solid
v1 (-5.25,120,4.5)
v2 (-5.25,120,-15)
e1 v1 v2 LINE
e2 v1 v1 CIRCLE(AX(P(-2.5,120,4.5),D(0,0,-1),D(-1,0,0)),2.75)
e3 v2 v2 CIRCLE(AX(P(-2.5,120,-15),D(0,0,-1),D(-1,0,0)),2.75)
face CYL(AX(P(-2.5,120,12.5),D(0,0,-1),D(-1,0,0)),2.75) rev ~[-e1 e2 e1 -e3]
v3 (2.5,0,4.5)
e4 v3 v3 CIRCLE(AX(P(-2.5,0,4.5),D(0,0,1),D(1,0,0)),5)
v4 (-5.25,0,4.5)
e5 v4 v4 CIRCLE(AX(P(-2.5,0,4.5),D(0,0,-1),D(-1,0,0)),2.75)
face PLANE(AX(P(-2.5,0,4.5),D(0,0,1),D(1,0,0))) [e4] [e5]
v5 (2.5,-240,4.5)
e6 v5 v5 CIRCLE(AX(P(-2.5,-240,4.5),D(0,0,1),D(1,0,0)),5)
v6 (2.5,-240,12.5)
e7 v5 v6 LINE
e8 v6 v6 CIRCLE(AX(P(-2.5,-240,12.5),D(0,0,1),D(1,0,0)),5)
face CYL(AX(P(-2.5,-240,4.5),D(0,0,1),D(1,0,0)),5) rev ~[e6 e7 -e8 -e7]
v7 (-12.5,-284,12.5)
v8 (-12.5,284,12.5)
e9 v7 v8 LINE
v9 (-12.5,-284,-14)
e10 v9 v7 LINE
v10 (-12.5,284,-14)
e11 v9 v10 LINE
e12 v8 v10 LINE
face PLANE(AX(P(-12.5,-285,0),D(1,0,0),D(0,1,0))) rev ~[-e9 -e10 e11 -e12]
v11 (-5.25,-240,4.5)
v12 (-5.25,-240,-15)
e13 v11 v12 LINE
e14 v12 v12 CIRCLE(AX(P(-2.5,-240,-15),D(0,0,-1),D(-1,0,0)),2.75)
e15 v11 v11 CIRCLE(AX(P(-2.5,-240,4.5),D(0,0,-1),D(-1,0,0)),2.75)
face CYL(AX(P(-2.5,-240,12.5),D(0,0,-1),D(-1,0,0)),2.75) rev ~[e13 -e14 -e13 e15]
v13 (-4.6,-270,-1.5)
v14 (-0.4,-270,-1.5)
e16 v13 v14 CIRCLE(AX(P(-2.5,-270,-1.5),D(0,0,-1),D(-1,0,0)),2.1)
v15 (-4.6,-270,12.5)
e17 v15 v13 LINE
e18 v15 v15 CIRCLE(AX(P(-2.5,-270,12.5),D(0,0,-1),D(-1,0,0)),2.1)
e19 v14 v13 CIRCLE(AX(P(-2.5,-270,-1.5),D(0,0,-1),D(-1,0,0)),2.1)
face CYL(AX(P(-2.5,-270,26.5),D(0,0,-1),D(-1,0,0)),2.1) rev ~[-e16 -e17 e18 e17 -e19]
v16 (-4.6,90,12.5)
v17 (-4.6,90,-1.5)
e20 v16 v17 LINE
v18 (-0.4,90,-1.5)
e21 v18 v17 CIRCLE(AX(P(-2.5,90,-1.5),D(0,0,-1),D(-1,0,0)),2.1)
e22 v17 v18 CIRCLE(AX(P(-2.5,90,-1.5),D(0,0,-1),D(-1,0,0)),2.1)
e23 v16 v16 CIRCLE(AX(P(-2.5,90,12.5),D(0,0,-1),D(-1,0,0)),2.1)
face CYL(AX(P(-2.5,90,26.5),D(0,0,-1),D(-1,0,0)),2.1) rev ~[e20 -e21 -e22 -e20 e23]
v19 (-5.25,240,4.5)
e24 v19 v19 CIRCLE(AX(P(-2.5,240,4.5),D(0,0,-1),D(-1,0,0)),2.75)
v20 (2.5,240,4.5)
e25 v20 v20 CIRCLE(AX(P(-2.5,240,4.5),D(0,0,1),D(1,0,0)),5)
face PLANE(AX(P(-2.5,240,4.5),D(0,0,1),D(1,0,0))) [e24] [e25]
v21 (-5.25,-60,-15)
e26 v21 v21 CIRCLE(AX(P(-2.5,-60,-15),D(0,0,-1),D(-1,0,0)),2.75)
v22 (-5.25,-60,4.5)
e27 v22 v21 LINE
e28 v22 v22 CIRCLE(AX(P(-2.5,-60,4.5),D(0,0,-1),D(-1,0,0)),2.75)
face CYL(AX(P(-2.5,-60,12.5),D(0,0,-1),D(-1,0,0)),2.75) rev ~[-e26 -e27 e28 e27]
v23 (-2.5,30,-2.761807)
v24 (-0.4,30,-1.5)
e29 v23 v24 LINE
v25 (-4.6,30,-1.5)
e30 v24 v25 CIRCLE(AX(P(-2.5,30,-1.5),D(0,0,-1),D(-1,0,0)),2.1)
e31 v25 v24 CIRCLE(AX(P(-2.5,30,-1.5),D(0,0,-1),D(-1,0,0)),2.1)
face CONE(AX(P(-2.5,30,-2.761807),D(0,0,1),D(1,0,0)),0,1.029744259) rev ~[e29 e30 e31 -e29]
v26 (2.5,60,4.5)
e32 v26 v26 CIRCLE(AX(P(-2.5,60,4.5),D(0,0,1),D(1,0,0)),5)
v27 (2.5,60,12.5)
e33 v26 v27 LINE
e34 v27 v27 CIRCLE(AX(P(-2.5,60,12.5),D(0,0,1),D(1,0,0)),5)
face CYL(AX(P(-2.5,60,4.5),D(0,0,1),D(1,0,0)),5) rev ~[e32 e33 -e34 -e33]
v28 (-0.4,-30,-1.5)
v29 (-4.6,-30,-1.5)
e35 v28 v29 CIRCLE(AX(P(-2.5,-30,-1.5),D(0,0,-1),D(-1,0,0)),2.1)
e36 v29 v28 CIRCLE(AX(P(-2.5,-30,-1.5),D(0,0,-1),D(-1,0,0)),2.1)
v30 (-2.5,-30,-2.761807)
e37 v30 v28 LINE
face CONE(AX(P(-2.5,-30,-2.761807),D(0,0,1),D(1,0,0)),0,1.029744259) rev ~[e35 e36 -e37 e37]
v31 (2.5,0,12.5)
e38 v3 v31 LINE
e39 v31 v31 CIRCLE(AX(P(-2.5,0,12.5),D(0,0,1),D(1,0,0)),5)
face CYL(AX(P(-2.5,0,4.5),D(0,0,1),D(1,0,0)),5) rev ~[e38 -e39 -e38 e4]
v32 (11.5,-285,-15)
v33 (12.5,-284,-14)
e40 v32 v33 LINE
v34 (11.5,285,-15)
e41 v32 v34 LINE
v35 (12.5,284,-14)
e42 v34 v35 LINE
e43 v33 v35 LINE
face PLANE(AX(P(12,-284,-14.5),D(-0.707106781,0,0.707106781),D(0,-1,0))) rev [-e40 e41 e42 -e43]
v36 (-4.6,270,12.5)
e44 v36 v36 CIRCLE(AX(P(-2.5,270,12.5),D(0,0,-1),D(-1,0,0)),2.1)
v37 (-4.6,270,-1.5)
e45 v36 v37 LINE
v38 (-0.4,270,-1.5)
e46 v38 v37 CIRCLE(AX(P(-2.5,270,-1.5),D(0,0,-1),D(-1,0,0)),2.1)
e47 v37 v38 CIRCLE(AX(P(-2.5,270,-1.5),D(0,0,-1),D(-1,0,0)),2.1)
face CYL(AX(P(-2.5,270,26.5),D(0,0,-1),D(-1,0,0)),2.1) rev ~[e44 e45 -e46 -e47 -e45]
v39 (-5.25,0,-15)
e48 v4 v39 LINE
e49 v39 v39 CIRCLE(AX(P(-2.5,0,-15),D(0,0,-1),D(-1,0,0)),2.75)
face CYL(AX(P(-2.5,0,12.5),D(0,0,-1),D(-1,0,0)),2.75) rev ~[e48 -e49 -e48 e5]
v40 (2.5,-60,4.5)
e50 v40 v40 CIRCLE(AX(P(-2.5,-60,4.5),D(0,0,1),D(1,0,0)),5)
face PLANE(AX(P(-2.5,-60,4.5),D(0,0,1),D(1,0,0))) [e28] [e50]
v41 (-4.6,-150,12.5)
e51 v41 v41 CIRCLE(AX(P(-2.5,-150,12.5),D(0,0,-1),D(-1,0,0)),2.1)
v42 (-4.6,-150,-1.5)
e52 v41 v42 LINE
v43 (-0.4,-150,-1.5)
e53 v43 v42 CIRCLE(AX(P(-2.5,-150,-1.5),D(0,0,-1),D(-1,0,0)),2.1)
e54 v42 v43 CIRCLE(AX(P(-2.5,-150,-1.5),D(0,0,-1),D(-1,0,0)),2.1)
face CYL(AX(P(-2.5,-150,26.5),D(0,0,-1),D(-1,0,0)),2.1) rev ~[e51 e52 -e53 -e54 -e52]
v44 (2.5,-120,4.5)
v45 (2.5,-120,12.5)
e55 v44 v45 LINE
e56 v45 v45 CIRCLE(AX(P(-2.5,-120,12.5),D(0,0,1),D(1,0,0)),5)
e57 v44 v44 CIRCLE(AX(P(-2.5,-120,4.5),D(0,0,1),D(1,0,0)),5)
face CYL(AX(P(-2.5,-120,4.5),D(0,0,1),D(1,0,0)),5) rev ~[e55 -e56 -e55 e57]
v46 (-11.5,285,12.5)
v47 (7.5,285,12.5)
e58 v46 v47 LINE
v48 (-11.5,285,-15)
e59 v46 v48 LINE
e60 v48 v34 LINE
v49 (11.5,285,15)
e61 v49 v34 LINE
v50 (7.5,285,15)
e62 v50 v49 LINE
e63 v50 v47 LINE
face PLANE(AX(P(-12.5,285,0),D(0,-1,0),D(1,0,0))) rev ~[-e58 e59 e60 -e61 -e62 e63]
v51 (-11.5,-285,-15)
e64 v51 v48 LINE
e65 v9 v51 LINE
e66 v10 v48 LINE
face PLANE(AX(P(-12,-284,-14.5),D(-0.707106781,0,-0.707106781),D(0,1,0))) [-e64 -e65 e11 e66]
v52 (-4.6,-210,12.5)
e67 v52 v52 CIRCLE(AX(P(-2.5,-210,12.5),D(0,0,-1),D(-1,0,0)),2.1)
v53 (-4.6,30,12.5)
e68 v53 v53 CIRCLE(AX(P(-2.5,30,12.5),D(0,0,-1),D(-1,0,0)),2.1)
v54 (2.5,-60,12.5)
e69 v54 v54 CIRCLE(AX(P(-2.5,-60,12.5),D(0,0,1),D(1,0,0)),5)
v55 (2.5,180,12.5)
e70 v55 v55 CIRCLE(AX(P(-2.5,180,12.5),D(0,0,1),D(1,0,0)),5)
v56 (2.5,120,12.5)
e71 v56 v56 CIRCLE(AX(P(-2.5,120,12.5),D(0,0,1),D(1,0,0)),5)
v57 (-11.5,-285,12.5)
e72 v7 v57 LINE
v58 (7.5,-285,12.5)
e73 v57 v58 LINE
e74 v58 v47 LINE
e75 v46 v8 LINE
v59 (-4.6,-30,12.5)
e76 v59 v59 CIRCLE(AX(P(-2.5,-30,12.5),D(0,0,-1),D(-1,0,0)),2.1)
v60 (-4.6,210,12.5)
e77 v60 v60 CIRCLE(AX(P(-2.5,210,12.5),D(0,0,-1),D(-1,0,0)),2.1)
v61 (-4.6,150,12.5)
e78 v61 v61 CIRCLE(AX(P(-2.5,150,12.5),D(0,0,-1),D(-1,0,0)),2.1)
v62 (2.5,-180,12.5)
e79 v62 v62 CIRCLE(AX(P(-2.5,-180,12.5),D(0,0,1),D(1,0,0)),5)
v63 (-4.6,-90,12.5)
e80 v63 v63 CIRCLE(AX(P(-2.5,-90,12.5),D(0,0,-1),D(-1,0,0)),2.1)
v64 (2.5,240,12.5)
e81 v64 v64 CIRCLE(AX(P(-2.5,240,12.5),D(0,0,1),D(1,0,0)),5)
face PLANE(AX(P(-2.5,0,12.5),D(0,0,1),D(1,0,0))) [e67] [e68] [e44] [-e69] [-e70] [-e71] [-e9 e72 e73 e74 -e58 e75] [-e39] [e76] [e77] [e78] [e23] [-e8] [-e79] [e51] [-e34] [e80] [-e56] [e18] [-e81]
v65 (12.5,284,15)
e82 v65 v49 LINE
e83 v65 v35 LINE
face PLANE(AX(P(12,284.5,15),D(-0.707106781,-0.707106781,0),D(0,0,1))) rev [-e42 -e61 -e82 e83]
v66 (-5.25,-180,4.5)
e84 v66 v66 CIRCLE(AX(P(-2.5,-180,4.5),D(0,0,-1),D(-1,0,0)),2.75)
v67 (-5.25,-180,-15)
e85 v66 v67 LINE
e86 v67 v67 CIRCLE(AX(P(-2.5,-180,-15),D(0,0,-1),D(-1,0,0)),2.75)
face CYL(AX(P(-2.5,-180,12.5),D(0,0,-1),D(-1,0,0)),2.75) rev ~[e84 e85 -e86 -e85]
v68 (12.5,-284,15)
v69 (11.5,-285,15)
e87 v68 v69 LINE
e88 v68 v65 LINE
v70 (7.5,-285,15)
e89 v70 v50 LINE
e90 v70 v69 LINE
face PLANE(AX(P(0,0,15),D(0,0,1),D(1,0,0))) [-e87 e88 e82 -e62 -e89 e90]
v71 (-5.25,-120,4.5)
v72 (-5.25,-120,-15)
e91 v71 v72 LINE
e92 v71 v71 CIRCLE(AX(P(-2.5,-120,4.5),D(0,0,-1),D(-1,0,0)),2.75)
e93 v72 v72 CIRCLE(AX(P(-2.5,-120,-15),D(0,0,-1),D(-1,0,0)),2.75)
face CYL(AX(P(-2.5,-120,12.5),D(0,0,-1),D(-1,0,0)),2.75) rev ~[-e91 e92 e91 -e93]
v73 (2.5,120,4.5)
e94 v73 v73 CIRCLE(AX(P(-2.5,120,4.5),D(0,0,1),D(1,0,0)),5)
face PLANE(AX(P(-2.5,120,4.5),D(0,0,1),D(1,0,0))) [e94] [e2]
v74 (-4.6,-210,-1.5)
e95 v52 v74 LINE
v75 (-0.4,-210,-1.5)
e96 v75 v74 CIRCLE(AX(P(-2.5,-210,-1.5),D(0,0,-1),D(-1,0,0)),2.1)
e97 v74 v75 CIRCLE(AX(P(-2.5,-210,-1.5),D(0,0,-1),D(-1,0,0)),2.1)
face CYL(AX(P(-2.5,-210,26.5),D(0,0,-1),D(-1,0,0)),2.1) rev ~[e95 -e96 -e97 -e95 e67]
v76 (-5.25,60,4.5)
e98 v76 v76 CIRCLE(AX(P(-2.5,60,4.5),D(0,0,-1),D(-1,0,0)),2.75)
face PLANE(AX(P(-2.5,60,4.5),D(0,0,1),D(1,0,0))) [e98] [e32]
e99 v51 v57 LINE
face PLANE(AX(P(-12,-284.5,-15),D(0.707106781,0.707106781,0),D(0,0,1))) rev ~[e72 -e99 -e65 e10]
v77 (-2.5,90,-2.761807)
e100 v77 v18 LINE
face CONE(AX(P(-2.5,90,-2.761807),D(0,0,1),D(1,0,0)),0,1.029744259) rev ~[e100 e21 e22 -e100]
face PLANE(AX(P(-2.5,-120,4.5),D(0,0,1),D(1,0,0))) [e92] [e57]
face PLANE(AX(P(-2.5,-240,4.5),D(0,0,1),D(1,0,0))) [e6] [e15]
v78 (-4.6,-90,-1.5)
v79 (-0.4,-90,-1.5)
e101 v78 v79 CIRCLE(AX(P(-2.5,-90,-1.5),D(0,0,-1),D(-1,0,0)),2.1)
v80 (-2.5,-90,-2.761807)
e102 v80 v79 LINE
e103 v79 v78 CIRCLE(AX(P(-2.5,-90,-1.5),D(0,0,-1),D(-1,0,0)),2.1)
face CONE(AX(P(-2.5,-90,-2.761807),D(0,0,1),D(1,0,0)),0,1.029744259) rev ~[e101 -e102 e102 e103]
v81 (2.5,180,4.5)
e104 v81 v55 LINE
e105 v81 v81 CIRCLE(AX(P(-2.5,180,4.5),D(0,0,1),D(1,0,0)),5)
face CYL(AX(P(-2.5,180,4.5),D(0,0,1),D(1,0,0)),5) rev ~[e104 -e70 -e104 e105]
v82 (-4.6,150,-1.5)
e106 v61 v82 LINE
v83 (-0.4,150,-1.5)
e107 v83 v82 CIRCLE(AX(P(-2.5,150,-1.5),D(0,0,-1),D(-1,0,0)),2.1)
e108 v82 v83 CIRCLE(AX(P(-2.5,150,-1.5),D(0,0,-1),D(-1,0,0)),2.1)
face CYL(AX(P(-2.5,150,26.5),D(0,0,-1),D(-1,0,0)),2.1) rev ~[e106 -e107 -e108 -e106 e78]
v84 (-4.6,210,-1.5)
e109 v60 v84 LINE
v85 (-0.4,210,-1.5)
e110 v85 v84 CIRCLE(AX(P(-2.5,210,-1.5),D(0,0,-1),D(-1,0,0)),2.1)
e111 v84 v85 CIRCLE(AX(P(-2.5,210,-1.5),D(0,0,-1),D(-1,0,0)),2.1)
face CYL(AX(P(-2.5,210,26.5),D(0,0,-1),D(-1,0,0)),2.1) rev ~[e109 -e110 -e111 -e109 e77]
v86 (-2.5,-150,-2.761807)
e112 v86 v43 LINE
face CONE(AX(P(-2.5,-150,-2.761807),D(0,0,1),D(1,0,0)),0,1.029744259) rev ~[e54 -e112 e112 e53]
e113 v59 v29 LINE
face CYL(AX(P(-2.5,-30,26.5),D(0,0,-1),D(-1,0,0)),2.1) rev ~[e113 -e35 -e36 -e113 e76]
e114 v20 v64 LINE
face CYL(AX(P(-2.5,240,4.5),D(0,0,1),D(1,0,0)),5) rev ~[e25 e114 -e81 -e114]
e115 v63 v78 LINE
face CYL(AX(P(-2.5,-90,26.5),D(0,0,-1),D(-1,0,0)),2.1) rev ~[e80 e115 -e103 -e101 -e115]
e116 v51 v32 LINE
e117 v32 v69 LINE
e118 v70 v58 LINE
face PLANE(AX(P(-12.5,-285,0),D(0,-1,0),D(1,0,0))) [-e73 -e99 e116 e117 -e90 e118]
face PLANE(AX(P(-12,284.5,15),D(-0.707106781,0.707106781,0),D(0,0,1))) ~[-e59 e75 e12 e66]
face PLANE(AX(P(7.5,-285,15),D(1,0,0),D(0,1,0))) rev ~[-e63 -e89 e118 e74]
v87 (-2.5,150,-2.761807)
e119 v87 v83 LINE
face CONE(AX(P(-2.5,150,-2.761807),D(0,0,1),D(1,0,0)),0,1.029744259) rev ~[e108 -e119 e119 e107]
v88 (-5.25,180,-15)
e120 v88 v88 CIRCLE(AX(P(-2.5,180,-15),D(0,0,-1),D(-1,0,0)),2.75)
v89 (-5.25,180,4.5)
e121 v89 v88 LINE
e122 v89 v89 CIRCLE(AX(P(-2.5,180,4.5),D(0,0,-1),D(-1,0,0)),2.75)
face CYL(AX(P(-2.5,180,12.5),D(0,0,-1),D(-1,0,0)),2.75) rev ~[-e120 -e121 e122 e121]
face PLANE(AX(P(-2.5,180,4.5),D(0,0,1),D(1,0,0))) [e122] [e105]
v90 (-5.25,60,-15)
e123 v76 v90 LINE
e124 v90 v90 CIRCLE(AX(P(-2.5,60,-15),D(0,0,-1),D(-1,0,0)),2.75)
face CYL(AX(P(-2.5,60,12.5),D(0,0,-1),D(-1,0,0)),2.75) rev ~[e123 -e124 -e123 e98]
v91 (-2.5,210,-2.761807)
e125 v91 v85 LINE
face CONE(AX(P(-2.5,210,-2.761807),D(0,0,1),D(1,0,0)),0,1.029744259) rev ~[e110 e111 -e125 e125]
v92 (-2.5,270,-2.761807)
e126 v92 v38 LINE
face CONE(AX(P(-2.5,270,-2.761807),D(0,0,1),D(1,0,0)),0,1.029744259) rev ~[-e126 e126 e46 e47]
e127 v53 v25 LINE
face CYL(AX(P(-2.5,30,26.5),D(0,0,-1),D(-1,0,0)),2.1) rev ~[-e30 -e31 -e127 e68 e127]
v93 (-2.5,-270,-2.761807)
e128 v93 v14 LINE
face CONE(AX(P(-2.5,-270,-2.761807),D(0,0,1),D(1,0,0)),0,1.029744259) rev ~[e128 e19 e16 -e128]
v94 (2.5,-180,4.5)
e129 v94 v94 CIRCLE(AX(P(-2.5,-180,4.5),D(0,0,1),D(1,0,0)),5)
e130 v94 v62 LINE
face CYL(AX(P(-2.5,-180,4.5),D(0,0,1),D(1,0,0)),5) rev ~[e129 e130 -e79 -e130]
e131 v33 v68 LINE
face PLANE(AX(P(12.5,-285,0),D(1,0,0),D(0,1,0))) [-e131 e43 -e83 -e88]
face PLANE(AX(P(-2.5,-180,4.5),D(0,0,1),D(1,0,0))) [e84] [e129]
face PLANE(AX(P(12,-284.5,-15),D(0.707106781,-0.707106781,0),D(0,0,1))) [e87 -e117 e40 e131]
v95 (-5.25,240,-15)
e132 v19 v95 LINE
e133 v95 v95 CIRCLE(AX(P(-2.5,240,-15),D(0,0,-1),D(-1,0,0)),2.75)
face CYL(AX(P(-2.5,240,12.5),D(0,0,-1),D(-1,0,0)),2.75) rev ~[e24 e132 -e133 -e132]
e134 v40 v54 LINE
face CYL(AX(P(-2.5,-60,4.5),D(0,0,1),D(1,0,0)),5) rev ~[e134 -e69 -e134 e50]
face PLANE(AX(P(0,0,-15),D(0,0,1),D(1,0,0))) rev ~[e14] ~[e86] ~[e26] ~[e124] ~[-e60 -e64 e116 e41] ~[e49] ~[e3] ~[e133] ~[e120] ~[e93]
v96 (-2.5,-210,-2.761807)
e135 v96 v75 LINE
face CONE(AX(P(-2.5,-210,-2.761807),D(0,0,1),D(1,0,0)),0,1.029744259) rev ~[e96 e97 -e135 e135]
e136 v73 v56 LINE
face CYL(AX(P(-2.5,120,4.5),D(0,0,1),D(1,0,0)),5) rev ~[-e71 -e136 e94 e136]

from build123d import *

# Parameters (mm, degrees)
SKETCH1_W                                           = 25
SKETCH1_H                                           = 570
EXTRUDE1_DEPTH                                      = 15
CHAMFER1_SIZE                                       = 1
SKETCH_1_W                                          = 20
SKETCH_1_H                                          = 570
CUT_EXTRUDE1_DEPTH                                  = 2.5
CHAMFER2_SIZE                                       = 1
M5_TAPPED_HOLE1_D                                   = 4.2
M5_TAPPED_HOLE1_DEPTH                               = 14
M5_TAPPED_HOLE1_TIP                                 = 1.2618073
HOLE_SIZE_PER_SOCKET_HEAD_CAP_SCREW_TYP_D           = 5.5
HOLE_SIZE_PER_SOCKET_HEAD_CAP_SCREW_TYP_CBORE_D     = 10
HOLE_SIZE_PER_SOCKET_HEAD_CAP_SCREW_TYP_CBORE_DEPTH = 8
LPATTERN1_COUNT                                     = 9
LPATTERN1_PITCH                                     = 60


with BuildPart() as part:
    # Sketch1 → Extrude1 (new, symmetric)
    with BuildSketch(Plane.XY):
        Rectangle(SKETCH1_W, SKETCH1_H)
    extrude(amount=EXTRUDE1_DEPTH, both=True)

    # Chamfer1
    chamfer1_edges = [part.edges().sort_by_distance(p)[0] for p in [
        (-12.5, 285, 0),
        (12.5, 285, 0),
        (12.5, -285, 0),
        (-12.5, -285, 0),
    ]]
    chamfer(chamfer1_edges, length=CHAMFER1_SIZE)

    # 草图1 → Cut-Extrude1 (cut)
    with BuildSketch(Plane.XY.offset(15)):
        with Locations((-2.5, 0)):
            Rectangle(SKETCH_1_W, SKETCH_1_H)
    extrude(amount=-CUT_EXTRUDE1_DEPTH, mode=Mode.SUBTRACT)

    # Chamfer2
    chamfer2_edges = [part.edges().sort_by_distance(p)[0] for p in [
        (12.5, 0, -15),
        (-12.5, 0, -15),
    ]]
    chamfer(chamfer2_edges, length=CHAMFER2_SIZE)

    # M5 Tapped Hole1
    with Locations(Plane.XY.offset(12.5)):
        with Locations((-2.5, -270), (-2.5, -210), (-2.5, -150), (-2.5, -90), (-2.5, -30), (-2.5, 30), (-2.5, 90), (-2.5, 150), (-2.5, 210), (-2.5, 270)):
            Hole(M5_TAPPED_HOLE1_D / 2, depth=M5_TAPPED_HOLE1_DEPTH)
            with Locations((0, 0, -(M5_TAPPED_HOLE1_DEPTH + M5_TAPPED_HOLE1_TIP / 2))):  # 118° drill point
                Cone(0, M5_TAPPED_HOLE1_D / 2, M5_TAPPED_HOLE1_TIP, mode=Mode.SUBTRACT)

    # Hole size (per socket head cap screw type)1 (through all)
    with Locations(Plane.XY.offset(12.5)):
        with Locations((-2.5, 240)):
            hole_size_per_socket_head_cap_screw_typ = CounterBoreHole(HOLE_SIZE_PER_SOCKET_HEAD_CAP_SCREW_TYP_D / 2, HOLE_SIZE_PER_SOCKET_HEAD_CAP_SCREW_TYP_CBORE_D / 2, HOLE_SIZE_PER_SOCKET_HEAD_CAP_SCREW_TYP_CBORE_DEPTH)

    # LPattern1: Hole size (per socket head cap screw type)1 ×9
    with Locations(*[(0, -i * LPATTERN1_PITCH, 0) for i in range(1, LPATTERN1_COUNT)]):
        add(hole_size_per_socket_head_cap_screw_typ, mode=Mode.SUBTRACT)


solid = part.part
